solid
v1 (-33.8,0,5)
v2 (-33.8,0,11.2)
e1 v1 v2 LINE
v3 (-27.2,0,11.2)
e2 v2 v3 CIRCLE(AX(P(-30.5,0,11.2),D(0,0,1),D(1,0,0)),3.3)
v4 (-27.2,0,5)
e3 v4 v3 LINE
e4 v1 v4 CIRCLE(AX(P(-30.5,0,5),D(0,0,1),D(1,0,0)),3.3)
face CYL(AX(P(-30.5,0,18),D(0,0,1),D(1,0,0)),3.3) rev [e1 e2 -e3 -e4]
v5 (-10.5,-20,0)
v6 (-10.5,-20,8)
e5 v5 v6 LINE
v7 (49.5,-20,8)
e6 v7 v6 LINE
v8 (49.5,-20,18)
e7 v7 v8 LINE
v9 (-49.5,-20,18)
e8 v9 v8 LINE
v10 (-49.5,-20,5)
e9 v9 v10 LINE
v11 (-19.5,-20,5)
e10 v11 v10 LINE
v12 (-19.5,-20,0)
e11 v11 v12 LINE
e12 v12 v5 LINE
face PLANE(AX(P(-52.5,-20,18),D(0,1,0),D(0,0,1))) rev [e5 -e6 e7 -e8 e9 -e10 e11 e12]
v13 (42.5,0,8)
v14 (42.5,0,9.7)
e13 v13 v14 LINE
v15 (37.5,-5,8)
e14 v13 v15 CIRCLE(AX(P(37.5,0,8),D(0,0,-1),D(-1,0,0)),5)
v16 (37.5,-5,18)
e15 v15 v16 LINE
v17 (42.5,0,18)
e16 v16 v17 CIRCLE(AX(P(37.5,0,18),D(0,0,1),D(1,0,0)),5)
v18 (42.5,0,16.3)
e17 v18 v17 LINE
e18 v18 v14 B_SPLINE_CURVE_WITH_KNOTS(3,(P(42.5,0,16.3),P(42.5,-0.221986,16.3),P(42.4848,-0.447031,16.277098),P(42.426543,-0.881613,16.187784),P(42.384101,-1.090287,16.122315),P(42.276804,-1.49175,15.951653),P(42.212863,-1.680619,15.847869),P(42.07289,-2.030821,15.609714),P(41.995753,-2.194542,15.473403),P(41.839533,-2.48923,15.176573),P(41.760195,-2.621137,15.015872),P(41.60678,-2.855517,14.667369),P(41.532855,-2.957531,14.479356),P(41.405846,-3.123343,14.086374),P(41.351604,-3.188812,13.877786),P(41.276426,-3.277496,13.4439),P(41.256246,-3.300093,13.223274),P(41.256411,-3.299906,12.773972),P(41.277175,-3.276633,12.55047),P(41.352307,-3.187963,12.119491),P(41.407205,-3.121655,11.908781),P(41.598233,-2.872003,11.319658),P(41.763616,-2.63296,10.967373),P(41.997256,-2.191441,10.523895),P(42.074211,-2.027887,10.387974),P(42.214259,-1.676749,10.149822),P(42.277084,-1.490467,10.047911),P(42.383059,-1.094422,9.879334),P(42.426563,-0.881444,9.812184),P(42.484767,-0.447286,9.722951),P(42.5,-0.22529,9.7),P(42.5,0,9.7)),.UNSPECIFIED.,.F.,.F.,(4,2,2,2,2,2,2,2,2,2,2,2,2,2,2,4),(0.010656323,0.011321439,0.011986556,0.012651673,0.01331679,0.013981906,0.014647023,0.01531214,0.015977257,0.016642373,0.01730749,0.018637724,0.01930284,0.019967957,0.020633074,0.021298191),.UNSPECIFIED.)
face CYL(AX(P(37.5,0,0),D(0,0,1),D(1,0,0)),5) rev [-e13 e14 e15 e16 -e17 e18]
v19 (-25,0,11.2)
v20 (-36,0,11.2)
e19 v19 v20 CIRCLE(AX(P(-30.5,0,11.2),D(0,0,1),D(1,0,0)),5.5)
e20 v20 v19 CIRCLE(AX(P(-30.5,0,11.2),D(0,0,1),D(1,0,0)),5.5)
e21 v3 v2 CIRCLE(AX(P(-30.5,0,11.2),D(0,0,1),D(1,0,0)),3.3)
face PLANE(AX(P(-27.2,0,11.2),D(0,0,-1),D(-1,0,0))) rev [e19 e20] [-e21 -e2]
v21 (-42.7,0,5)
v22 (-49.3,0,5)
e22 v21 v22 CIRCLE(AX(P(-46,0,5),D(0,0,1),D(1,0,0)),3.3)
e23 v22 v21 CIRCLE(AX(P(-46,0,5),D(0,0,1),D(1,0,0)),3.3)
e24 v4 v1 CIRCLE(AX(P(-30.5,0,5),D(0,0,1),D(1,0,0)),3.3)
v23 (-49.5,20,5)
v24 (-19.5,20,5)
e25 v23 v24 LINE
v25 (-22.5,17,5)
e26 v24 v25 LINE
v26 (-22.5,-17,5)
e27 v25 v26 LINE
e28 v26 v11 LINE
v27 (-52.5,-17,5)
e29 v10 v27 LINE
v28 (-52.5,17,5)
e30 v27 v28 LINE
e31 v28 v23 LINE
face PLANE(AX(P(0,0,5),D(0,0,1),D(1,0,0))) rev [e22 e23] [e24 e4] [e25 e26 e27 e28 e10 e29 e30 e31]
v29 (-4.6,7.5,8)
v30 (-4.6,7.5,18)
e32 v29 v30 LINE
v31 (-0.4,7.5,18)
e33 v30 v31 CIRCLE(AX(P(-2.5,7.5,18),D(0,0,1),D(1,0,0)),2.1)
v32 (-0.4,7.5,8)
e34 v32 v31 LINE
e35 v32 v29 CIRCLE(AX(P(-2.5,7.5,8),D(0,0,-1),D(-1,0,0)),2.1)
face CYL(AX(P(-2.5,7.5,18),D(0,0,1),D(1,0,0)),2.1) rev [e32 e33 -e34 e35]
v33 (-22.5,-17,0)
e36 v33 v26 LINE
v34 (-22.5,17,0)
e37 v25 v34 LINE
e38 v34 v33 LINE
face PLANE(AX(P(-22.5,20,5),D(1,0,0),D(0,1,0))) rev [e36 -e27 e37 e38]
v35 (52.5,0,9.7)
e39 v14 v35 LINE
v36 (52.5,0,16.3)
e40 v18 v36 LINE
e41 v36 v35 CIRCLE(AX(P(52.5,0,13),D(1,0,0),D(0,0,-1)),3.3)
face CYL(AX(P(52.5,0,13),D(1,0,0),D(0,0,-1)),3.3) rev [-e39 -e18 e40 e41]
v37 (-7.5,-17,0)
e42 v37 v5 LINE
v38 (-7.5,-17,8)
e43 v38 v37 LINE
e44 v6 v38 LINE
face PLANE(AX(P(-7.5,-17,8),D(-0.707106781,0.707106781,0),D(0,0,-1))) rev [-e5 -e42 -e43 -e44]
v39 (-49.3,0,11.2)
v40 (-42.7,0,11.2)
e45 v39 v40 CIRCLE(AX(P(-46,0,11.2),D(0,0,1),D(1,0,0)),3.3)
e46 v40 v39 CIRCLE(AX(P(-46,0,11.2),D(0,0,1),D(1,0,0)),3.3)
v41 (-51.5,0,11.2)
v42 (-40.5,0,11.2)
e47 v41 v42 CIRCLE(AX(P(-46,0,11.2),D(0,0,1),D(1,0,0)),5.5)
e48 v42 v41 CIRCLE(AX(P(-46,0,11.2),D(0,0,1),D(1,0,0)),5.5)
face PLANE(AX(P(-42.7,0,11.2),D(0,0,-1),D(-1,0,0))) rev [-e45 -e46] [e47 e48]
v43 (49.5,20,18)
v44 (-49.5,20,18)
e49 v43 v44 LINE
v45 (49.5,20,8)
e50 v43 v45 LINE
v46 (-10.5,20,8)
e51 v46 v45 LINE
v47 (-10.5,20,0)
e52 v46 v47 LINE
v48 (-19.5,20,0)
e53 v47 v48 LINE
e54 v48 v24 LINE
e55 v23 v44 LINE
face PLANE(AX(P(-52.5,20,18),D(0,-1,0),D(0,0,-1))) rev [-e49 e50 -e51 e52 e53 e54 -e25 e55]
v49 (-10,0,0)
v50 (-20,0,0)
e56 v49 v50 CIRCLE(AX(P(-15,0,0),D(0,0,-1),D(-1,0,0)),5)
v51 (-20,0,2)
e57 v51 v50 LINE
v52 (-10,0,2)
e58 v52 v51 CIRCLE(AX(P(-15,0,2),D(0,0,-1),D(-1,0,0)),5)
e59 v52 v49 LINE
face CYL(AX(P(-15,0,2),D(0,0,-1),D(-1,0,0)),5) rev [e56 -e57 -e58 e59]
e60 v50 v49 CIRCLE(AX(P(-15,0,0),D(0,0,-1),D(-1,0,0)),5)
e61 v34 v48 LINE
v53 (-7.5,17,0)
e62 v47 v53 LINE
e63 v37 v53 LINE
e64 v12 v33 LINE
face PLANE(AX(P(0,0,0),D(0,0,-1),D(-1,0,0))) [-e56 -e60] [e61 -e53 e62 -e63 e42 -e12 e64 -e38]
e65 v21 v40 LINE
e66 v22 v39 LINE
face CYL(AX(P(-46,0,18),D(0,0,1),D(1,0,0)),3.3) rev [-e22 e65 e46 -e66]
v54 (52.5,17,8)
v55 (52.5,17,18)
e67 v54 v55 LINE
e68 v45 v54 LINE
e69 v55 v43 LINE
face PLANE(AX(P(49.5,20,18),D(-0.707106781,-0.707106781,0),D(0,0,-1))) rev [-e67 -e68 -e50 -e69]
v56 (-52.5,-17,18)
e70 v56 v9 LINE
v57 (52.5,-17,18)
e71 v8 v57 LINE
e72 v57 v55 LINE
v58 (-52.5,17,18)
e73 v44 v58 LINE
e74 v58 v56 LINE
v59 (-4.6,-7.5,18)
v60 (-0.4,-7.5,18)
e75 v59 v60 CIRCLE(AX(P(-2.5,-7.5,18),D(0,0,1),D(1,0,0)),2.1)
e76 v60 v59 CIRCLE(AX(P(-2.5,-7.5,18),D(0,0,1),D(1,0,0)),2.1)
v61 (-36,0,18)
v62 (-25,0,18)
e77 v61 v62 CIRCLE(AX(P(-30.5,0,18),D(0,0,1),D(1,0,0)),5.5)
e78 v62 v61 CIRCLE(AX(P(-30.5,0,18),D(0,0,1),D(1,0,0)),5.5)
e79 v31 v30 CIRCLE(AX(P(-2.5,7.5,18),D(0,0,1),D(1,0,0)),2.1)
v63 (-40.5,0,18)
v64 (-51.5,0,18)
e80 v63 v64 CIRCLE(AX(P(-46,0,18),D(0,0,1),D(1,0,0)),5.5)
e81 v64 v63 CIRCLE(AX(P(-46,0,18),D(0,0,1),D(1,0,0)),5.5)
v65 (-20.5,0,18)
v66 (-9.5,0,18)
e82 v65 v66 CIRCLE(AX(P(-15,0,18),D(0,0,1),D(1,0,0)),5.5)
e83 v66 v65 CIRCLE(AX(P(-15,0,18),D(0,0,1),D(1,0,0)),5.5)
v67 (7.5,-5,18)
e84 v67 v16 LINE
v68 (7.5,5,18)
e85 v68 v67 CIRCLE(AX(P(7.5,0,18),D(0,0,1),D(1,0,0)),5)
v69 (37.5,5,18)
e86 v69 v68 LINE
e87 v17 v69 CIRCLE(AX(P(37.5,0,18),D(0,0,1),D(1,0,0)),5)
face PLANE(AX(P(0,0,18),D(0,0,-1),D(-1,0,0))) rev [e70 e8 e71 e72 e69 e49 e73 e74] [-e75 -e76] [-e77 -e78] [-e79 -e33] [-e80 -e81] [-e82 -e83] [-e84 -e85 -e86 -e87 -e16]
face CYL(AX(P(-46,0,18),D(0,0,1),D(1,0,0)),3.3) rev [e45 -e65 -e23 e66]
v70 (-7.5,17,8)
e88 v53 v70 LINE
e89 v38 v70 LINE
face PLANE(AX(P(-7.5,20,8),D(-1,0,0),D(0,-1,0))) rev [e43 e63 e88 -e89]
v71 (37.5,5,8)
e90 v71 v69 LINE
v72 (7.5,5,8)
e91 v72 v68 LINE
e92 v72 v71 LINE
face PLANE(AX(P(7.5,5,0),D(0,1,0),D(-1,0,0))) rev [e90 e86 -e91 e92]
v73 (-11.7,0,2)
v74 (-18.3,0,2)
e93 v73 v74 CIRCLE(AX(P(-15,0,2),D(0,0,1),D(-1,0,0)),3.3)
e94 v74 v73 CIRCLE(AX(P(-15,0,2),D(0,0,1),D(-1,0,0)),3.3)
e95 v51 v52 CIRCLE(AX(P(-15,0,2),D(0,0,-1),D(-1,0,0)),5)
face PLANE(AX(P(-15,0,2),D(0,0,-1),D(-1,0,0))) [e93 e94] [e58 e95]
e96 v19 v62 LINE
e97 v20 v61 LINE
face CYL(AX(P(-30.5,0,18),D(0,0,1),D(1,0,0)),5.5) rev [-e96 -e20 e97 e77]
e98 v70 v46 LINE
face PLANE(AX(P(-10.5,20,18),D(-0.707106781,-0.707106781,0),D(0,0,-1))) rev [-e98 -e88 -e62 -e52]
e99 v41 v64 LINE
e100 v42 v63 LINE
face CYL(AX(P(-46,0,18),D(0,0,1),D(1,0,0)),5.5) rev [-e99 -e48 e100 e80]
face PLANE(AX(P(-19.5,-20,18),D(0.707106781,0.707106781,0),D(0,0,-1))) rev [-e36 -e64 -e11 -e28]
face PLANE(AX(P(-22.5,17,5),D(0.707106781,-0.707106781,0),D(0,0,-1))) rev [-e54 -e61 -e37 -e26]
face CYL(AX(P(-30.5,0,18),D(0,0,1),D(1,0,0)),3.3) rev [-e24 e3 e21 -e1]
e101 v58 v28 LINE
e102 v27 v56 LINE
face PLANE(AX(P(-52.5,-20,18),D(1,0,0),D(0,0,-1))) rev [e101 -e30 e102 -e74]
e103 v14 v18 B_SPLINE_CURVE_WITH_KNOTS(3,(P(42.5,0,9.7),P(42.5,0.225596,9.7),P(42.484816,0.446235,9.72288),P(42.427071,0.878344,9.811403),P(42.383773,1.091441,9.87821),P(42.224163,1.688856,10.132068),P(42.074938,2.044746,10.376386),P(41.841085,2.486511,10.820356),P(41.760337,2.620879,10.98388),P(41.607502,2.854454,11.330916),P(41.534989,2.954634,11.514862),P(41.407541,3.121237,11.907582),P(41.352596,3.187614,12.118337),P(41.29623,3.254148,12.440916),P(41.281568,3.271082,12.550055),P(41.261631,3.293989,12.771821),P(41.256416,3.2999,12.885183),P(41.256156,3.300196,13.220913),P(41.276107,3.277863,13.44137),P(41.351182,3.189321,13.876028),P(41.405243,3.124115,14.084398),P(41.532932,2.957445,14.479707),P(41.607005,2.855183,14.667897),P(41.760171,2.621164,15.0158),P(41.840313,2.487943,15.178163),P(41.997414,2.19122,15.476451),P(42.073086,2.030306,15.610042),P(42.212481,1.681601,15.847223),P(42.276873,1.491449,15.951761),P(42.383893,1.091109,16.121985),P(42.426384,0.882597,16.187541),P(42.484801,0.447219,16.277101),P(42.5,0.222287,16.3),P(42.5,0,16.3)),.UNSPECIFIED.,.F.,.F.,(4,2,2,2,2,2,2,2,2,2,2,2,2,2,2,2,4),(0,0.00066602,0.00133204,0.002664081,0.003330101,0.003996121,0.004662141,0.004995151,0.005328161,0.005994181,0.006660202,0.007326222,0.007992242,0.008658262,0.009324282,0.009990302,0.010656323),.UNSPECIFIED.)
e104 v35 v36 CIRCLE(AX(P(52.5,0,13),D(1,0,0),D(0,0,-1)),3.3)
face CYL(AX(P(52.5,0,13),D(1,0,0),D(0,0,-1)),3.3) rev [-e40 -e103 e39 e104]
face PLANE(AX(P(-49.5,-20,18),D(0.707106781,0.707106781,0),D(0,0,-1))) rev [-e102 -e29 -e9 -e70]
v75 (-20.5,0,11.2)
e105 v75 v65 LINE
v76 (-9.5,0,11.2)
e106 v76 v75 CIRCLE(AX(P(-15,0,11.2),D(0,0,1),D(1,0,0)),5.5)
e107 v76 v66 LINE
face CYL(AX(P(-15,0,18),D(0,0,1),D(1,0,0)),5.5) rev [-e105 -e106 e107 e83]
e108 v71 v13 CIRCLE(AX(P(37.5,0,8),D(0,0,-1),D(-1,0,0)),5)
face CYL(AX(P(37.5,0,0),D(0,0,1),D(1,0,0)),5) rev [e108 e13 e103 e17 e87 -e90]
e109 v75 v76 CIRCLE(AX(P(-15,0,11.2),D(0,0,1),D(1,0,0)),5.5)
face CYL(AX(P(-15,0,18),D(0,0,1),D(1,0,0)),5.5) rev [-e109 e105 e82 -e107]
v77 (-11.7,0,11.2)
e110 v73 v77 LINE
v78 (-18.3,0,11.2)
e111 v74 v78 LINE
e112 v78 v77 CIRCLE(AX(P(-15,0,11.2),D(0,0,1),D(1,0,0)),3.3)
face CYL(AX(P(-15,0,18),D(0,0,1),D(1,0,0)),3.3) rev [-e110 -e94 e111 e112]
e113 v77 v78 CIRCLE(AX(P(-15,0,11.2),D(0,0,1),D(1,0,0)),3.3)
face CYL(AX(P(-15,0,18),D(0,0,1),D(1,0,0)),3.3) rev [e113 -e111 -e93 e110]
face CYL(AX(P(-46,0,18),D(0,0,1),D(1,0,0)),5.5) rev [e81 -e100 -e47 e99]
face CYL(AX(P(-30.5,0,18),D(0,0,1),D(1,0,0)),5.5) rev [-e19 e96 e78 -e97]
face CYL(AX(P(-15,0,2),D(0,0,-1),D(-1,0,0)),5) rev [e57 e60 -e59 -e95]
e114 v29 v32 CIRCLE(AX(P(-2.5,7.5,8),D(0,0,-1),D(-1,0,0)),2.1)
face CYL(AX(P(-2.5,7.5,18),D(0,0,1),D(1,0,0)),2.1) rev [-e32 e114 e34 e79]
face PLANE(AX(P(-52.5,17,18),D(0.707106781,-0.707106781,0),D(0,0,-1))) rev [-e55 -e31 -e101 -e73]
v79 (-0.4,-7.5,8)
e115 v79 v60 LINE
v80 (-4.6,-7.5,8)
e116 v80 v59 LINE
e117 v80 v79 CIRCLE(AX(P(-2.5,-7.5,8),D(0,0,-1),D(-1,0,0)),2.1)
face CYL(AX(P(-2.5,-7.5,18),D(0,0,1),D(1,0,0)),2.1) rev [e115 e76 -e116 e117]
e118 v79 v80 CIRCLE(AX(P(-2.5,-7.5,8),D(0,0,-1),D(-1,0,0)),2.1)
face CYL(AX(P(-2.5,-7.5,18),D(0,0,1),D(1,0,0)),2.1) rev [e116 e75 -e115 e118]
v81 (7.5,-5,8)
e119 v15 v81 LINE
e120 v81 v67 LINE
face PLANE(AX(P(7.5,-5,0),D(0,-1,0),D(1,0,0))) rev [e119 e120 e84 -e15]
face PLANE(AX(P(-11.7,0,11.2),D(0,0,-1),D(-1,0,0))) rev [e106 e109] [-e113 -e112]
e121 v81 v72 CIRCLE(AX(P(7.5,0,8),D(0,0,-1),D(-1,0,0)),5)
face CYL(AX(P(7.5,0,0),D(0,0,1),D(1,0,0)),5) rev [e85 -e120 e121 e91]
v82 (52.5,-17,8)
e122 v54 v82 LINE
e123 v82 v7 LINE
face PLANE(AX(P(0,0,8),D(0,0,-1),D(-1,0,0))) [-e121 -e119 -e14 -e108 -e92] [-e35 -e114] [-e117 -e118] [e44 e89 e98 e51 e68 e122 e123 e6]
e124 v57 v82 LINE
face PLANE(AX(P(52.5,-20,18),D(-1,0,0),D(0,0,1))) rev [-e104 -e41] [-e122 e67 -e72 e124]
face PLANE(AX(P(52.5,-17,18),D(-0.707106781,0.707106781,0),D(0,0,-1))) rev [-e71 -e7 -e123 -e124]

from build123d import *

# Parameters (mm, degrees)
SKETCH_1_W                = 105
SKETCH_1_H                = 40
EXTRUDE_1_DEPTH           = 18
SKETCH_2_W                = 30
SKETCH_2_H                = 40
CUT_EXTRUDE_1_DEPTH       = 5
SKETCH_3_W                = 60
SKETCH_3_H                = 40
CUT_EXTRUDE_2_DEPTH       = 8
HOLE_WIZARD_1_D           = 6.6
HOLE_WIZARD_1_CBORE_D     = 11
HOLE_WIZARD_1_CBORE_DEPTH = 6.8
SKETCH_6_R                = 5
CUT_EXTRUDE_3_DEPTH       = 2
CHAMFER_1_SIZE            = 3
CUT_EXTRUDE_4_DEPTH       = 59.993643725
HOLE_WIZARD_M6_1_REACH    = 110.393
HOLE_WIZARD_M6_1_BORE_R   = 3.3
HOLE_WIZARD_M5_1_D        = 4.2


with BuildPart() as part:
    # 草图1 → 凸台-拉伸1 (new body)
    with BuildSketch(Plane.XY):
        Rectangle(SKETCH_1_W, SKETCH_1_H)
    extrude(amount=EXTRUDE_1_DEPTH)

    # 草图2 → 切除-拉伸1 (cut)
    with BuildSketch(Plane(origin=(0, 0, 0), x_dir=(-1, 0, 0), z_dir=(0, 0, -1))):
        with Locations((37.5, 0)):
            Rectangle(SKETCH_2_W, SKETCH_2_H)
    extrude(amount=-CUT_EXTRUDE_1_DEPTH, mode=Mode.SUBTRACT)

    # 草图3 → 切除-拉伸2 (cut)
    with BuildSketch(Plane(origin=(0, 0, 0), x_dir=(-1, 0, 0), z_dir=(0, 0, -1))):
        with Locations((-22.5, 0)):
            Rectangle(SKETCH_3_W, SKETCH_3_H)
    extrude(amount=-CUT_EXTRUDE_2_DEPTH, mode=Mode.SUBTRACT)

    # 打孔尺寸(%根据)内六角圆柱头螺钉的类型1 (through all)
    with Locations(Plane.XY.offset(18)):
        with Locations((-46, 0), (-30.5, 0), (-15, 0)):
            CounterBoreHole(HOLE_WIZARD_1_D / 2, HOLE_WIZARD_1_CBORE_D / 2, HOLE_WIZARD_1_CBORE_DEPTH)

    # 草图6 → 切除-拉伸3 (cut)
    with BuildSketch(Plane(origin=(0, 0, 0), x_dir=(-1, 0, 0), z_dir=(0, 0, -1))):
        with Locations((15, 0)):
            Circle(SKETCH_6_R)
    extrude(amount=-CUT_EXTRUDE_3_DEPTH, mode=Mode.SUBTRACT)

    # 倒角1
    chamfer_1_edges = [part.edges().sort_by_distance(p)[0] for p in [
        (-22.5, -20, 2.5),
        (-22.5, 20, 2.5),
        (-7.5, 20, 4),
        (-7.5, -20, 4),
        (52.5, -20, 13),
        (-52.5, -20, 11.5),
        (-52.5, 20, 11.5),
        (52.5, 20, 13),
    ]]
    chamfer(chamfer_1_edges, length=CHAMFER_1_SIZE)

    # 草图7 → 切除-拉伸4 (cut, through all)
    with BuildSketch(Plane.XY.offset(18)):
        with BuildLine():
            Line((7.5, 5), (37.5, 5))
            ThreePointArc((37.5, 5), (42.5, 0), (37.5, -5))
            Line((37.5, -5), (7.5, -5))
            ThreePointArc((7.5, -5), (2.5, 0), (7.5, 5))
        make_face()
    extrude(amount=-CUT_EXTRUDE_4_DEPTH, mode=Mode.SUBTRACT)

    # M6 间隙孔1 bore → M6 间隙孔1 (cut, up to next)
    with BuildSketch(Plane(origin=(52.5, 0, 0), x_dir=(0, 0, -1), z_dir=(1, 0, 0)), mode=Mode.PRIVATE) as hole_wizard_m6_1_sk1:
        with Locations((-13, 0)):
            Circle(HOLE_WIZARD_M6_1_BORE_R)
    hole_wizard_m6_1_tool1 = extrude(hole_wizard_m6_1_sk1.sketch, amount=-HOLE_WIZARD_M6_1_REACH, mode=Mode.PRIVATE) & part.part
    add(hole_wizard_m6_1_tool1.solids().sort_by_distance((52.5, 0, 13))[0], mode=Mode.SUBTRACT)

    # M5 螺纹孔1 (through all)
    with Locations(Plane.XY.offset(18)):
        with Locations((-2.5, 7.5), (-2.5, -7.5)):
            Hole(HOLE_WIZARD_M5_1_D / 2)


solid = part.part
